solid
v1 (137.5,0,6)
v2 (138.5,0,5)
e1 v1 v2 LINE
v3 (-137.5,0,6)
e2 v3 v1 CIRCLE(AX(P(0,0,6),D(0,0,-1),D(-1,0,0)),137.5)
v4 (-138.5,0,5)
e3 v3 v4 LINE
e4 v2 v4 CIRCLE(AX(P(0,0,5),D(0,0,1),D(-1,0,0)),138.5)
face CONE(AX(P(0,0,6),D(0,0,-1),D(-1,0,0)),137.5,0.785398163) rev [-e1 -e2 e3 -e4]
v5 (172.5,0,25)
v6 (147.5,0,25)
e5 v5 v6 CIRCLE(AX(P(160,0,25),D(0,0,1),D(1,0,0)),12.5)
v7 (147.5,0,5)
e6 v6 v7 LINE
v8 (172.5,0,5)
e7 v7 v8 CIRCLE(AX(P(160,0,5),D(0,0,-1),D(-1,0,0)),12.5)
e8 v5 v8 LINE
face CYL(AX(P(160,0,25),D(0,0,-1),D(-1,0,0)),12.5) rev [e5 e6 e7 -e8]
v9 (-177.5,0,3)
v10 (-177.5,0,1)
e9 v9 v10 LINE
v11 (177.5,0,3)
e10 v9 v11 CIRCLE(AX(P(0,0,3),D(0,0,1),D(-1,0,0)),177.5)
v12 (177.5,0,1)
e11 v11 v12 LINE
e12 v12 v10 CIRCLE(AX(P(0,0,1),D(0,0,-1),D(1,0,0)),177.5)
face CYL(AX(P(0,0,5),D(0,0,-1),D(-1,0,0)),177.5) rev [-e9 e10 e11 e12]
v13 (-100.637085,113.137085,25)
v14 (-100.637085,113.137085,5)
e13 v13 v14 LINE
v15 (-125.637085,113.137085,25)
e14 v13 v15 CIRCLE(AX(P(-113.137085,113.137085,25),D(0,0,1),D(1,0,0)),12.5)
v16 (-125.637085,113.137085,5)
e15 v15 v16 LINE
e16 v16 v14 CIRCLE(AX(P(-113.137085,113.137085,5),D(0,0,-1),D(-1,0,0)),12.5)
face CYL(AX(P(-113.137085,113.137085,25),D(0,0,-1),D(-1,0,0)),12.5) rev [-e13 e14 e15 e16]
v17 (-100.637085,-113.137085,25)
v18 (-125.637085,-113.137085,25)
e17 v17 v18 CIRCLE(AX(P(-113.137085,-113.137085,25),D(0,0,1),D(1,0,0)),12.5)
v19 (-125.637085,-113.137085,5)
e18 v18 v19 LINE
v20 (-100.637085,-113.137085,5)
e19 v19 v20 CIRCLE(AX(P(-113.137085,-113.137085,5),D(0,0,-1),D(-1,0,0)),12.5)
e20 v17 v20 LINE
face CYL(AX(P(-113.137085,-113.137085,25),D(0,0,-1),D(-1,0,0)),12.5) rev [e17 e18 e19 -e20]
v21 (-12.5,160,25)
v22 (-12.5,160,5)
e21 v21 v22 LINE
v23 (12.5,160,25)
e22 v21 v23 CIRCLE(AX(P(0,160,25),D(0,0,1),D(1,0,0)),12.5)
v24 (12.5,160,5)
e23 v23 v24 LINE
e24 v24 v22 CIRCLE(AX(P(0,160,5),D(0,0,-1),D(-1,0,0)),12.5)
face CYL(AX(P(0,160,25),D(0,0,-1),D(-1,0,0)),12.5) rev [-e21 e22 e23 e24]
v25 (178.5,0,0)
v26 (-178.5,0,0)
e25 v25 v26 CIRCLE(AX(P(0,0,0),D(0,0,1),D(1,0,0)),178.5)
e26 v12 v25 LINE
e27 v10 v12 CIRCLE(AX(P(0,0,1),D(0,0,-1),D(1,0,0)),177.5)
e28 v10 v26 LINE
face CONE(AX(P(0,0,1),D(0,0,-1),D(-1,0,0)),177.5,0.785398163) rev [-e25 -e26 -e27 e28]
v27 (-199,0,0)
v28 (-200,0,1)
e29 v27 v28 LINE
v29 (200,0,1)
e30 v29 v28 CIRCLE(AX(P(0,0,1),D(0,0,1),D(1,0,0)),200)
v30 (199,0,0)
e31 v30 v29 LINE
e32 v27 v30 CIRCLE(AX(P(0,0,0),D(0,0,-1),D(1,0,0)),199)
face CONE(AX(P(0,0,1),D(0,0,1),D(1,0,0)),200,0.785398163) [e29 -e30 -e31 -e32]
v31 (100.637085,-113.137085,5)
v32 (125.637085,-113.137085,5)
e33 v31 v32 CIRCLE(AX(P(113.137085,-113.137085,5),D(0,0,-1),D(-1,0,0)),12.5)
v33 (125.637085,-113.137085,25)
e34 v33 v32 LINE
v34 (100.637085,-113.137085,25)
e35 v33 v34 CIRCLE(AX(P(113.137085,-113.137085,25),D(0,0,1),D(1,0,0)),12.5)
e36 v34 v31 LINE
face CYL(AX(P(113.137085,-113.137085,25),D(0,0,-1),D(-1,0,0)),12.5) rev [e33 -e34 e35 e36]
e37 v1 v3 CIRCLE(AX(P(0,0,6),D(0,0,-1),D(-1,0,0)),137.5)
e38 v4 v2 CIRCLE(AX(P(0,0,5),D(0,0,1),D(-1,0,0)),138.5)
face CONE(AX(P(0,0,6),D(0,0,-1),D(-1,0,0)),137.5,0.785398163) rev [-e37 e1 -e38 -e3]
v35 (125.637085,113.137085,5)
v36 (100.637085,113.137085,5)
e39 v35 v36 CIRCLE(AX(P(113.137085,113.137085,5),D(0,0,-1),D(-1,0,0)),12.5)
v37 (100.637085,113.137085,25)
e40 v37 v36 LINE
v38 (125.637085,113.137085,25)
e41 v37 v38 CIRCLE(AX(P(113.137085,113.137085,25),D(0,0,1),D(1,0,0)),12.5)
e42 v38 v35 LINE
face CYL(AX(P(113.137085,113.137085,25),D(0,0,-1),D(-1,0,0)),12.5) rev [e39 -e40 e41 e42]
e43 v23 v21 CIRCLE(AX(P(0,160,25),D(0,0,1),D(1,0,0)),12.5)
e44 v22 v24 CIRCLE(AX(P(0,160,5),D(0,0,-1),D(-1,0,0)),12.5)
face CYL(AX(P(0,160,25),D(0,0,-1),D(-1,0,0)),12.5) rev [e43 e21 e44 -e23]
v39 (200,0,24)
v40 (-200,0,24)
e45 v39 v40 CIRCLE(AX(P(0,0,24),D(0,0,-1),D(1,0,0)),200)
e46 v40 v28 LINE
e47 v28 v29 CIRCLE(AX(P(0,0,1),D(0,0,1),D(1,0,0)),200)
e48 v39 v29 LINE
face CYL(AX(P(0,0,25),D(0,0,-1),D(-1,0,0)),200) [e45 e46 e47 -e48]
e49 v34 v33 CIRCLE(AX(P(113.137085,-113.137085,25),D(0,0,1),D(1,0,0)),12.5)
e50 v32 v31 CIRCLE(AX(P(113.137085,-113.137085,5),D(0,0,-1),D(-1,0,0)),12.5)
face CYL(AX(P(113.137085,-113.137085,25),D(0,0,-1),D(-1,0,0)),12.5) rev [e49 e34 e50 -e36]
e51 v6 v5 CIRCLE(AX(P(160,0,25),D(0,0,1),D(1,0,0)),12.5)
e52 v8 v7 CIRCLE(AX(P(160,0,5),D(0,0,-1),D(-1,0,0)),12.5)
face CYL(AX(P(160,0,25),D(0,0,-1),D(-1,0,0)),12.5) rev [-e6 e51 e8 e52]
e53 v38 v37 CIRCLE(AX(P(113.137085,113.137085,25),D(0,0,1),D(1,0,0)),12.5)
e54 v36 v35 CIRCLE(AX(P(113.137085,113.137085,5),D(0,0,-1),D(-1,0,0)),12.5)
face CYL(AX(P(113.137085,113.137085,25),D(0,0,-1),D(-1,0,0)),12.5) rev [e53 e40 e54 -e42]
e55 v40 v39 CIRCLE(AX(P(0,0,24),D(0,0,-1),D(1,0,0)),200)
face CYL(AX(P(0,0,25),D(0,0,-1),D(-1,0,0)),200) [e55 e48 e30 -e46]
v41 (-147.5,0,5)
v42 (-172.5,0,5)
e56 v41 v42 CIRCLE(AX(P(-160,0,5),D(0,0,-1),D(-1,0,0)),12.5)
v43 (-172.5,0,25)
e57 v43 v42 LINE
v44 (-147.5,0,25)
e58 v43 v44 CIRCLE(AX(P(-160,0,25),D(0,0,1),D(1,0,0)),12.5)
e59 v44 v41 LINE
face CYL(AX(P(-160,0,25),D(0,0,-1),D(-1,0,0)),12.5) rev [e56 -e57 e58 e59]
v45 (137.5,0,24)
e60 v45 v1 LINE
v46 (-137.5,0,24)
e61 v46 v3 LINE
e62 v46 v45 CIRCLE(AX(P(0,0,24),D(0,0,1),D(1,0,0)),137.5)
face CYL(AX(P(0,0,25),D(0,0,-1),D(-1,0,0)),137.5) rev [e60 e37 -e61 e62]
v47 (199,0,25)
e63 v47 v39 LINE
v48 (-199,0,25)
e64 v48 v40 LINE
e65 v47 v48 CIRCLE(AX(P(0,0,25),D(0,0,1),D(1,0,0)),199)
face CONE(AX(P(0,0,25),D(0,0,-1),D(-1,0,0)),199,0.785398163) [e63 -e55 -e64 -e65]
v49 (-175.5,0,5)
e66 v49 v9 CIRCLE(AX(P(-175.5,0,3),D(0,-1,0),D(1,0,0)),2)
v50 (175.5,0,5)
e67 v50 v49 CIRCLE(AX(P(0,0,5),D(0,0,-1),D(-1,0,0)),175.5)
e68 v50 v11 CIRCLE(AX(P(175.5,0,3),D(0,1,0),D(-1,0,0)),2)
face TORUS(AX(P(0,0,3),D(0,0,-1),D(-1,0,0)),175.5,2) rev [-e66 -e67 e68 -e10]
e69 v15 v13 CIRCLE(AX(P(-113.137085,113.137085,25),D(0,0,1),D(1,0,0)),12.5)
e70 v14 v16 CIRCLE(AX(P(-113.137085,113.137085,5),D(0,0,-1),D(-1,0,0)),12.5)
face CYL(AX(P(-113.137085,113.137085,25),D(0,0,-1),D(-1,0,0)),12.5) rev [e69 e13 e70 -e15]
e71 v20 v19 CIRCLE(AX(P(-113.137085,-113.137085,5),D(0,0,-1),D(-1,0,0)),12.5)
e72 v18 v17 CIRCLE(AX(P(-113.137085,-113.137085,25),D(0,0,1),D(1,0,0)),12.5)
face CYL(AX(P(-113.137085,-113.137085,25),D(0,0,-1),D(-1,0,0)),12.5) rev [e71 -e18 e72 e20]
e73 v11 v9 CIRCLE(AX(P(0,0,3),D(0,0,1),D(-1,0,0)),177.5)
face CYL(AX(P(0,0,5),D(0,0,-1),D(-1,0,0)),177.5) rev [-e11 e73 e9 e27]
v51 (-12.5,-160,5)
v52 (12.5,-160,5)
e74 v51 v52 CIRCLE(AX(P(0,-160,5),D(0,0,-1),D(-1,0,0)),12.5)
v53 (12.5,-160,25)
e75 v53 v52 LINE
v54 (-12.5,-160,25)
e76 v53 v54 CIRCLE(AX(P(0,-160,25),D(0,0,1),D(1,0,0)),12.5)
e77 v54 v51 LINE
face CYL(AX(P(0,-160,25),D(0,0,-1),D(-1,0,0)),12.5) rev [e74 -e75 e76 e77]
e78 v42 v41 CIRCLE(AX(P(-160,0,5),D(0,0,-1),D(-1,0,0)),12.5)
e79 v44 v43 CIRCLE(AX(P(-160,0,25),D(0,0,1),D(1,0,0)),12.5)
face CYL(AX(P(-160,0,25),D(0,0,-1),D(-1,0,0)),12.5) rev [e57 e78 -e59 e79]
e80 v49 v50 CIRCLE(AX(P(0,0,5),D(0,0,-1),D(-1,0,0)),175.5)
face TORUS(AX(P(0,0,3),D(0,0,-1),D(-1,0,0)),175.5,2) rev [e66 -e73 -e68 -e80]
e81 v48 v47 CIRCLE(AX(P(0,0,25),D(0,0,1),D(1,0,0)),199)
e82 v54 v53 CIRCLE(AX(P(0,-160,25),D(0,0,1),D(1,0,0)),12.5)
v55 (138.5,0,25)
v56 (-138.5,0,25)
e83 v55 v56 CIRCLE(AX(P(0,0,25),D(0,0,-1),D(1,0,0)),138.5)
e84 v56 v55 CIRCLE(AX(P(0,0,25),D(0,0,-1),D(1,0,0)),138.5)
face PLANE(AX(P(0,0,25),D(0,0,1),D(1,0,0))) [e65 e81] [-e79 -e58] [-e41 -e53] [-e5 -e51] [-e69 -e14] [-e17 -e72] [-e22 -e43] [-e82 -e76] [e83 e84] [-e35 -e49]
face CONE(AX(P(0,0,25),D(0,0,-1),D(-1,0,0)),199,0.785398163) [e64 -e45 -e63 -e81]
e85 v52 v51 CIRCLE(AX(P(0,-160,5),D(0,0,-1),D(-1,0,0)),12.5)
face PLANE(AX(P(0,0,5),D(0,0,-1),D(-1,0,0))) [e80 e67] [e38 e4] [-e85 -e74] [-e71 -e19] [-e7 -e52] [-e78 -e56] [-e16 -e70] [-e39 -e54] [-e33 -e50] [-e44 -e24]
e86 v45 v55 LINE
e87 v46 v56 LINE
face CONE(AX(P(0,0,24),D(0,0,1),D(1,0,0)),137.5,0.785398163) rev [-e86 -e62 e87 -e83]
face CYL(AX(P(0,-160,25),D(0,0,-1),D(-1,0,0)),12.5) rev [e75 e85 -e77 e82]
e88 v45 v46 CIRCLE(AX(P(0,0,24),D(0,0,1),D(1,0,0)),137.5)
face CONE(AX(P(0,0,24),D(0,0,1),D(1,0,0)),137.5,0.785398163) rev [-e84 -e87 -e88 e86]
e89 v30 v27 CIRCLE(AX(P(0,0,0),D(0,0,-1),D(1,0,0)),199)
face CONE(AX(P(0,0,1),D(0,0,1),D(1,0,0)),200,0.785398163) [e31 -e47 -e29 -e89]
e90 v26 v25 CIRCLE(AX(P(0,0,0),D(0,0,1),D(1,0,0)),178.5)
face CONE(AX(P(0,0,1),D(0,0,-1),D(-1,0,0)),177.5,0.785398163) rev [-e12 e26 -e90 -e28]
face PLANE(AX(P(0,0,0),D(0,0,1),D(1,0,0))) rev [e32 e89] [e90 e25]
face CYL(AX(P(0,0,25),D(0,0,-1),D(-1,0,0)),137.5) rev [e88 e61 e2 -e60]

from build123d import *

# Parameters (mm, degrees)
SKETCH1_R           = 200
SKETCH1_R_2         = 137.5
SKETCH1_R_3         = 12.5
BOSS_EXTRUDE1_DEPTH = 25
CHAMFER1_SIZE       = 1
SKETCH4_R           = 177.5
CUT_EXTRUDE2_DEPTH  = 5
FILLET1_R           = 2
CHAMFER2_SIZE       = 1


with BuildPart() as part:
    # Sketch1 → Boss-Extrude1 (new body)
    with BuildSketch(Plane.XY):
        Circle(SKETCH1_R)
        Circle(SKETCH1_R_2, mode=Mode.SUBTRACT)
        with Locations((0, 160)):
            Circle(SKETCH1_R_3, mode=Mode.SUBTRACT)
        with Locations((113.13708499, 113.13708499)):
            Circle(SKETCH1_R_3, mode=Mode.SUBTRACT)
        with Locations((160, 0)):
            Circle(SKETCH1_R_3, mode=Mode.SUBTRACT)
        with Locations((113.13708499, -113.13708499)):
            Circle(SKETCH1_R_3, mode=Mode.SUBTRACT)
        with Locations((0, -160)):
            Circle(SKETCH1_R_3, mode=Mode.SUBTRACT)
        with Locations((-113.13708499, -113.13708499)):
            Circle(SKETCH1_R_3, mode=Mode.SUBTRACT)
        with Locations((-160, 0)):
            Circle(SKETCH1_R_3, mode=Mode.SUBTRACT)
        with Locations((-113.13708499, 113.13708499)):
            Circle(SKETCH1_R_3, mode=Mode.SUBTRACT)
    extrude(amount=BOSS_EXTRUDE1_DEPTH)

    # Chamfer1
    chamfer1_edges = [part.edges().sort_by_distance(p)[0] for p in [
        (-200, 0, 0),
        (-200, 0, 25),
        (-137.5, 0, 0),
        (-137.5, 0, 25),
    ]]
    chamfer(chamfer1_edges, length=CHAMFER1_SIZE)

    # Sketch4 → Cut-Extrude2 (cut)
    with BuildSketch(Plane(origin=(0, 0, 0), x_dir=(-1, 0, 0), z_dir=(0, 0, -1))):
        Circle(SKETCH4_R)
    extrude(amount=-CUT_EXTRUDE2_DEPTH, mode=Mode.SUBTRACT)

    # Fillet1
    fillet1_edges = [part.edges().sort_by_distance(p)[0] for p in [
        (177.5, 0, 5),
    ]]
    fillet(fillet1_edges, radius=FILLET1_R)

    # Chamfer2
    chamfer2_edges = [part.edges().sort_by_distance(p)[0] for p in [
        (-137.5, 0, 5),
        (177.5, 0, 0),
    ]]
    chamfer(chamfer2_edges, length=CHAMFER2_SIZE)


solid = part.part
